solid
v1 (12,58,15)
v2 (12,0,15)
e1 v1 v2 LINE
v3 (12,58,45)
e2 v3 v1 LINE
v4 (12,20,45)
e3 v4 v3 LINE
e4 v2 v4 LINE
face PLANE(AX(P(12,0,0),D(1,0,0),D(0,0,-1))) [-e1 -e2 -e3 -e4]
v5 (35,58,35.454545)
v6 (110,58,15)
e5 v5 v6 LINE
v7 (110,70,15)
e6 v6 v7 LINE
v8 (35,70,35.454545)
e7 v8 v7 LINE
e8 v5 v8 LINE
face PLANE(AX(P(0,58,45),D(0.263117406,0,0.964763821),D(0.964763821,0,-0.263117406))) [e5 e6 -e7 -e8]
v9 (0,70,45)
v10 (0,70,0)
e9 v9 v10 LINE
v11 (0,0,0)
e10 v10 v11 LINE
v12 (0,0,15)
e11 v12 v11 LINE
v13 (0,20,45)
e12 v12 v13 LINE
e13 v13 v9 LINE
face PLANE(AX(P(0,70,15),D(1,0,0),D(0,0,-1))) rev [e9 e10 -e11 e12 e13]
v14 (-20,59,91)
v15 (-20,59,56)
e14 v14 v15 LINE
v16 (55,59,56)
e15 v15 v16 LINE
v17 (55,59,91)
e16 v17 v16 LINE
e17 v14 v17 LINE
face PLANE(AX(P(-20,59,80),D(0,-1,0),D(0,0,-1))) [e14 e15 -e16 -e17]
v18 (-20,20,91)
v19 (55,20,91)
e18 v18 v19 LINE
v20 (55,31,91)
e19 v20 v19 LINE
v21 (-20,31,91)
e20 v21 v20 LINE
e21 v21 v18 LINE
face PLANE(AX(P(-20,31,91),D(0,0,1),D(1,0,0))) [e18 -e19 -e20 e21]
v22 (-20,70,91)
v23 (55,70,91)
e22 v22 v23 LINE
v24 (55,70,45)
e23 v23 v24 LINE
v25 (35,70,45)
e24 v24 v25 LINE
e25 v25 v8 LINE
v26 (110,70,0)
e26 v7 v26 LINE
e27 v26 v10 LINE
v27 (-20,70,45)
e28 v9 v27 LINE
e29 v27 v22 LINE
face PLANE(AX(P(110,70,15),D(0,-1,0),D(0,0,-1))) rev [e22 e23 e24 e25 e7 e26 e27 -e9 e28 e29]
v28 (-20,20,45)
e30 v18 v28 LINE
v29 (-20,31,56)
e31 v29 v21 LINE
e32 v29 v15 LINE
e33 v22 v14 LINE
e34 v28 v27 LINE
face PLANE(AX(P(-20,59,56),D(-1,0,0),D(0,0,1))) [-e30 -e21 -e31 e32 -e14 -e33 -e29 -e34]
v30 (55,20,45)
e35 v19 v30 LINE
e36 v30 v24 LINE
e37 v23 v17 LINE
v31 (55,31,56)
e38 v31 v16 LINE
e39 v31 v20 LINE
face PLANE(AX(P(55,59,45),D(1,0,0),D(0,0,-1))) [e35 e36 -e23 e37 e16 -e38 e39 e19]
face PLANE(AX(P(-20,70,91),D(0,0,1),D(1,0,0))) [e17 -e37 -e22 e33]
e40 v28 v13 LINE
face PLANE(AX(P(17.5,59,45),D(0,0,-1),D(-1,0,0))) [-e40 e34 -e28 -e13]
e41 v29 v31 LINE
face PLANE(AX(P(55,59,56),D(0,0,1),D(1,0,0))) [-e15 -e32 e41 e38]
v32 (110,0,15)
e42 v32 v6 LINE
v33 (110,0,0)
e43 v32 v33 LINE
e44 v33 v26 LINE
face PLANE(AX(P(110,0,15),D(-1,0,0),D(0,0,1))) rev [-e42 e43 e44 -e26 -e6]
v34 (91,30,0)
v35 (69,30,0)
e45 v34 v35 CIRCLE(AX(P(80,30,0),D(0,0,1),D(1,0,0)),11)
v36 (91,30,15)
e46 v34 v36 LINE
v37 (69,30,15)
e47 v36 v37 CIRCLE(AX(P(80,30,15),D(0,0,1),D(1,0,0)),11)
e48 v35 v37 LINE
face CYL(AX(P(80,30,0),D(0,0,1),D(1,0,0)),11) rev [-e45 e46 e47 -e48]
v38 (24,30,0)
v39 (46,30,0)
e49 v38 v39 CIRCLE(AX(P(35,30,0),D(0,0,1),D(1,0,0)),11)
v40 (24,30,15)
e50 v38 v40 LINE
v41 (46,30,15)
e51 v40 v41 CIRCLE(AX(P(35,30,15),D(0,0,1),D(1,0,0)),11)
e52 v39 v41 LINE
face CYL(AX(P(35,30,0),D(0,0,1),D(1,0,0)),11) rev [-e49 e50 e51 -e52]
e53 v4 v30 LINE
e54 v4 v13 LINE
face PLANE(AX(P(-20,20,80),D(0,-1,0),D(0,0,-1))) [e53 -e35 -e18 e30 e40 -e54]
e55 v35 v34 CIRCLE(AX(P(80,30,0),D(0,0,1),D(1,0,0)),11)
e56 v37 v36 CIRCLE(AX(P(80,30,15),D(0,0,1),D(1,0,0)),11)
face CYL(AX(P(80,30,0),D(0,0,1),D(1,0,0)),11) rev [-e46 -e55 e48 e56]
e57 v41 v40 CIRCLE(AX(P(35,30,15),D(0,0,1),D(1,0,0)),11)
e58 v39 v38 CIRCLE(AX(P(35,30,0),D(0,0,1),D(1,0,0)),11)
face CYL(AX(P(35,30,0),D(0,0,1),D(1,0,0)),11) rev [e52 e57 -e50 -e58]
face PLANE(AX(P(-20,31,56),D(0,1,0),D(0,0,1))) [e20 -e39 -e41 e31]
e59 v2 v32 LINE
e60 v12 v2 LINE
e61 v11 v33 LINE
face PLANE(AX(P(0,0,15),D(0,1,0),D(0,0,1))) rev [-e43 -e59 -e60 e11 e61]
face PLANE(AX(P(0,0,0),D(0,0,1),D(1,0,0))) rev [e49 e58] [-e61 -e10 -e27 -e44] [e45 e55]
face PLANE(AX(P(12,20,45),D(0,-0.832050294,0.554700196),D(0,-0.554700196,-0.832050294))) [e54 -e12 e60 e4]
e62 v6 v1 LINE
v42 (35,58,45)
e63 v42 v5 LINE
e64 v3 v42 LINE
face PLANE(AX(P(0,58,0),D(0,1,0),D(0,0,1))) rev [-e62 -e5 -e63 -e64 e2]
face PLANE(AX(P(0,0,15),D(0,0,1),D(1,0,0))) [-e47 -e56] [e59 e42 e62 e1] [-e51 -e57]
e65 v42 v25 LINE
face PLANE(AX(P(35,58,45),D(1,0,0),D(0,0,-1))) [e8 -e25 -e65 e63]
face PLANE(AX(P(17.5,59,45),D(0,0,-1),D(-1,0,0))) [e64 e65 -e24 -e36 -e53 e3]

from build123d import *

# Parameters (mm, degrees)
BASE_PLATE_SKETCH_W         = 110
BASE_PLATE_SKETCH_H         = 70
BASE_PLATE_15MM_DEPTH       = 15
TRIANGULAR_WALL_12MM_DEPTH  = 12
WALL_EXTENSION_12MM_DEPTH   = 12
WEDGE_GUSSET_12MM_DEPTH     = 12
TOP_PROFILE_BOSS_11MM_DEPTH = 11
PROFILE_ARM_75MM_DEPTH      = 75
BLOCK_ARM_SKETCH_W          = 24
BLOCK_ARM_SKETCH_H          = 11
BLOCK_ARM_75MM_DEPTH        = 75
HOLE_CIRCLES_2X_22_SKETCH_R = 11
HOLES_2X_22_DEPTH           = 15
UPPER_JAW_SKETCH_W          = 11
UPPER_JAW_SKETCH_H          = 11
UPPER_JAW_75MM_DEPTH        = 75
LOWER_JAW_SKETCH_W          = 11
LOWER_JAW_SKETCH_H          = 11
LOWER_JAW_75MM_DEPTH        = 75


with BuildPart() as part:
    # Base Plate Sketch → Base Plate 15mm (new body)
    with BuildSketch(Plane.XY):
        with Locations((55, 35)):
            Rectangle(BASE_PLATE_SKETCH_W, BASE_PLATE_SKETCH_H)
    extrude(amount=BASE_PLATE_15MM_DEPTH)

    # Triangular Wall Sketch → Triangular Wall 12mm (add)
    with BuildSketch(Plane(origin=(0, 70, 0), x_dir=(1, 0, 0), z_dir=(0, 1, 0))):
        Polygon((0, -15), (0, -45), (110, -15), align=None)
    extrude(amount=-TRIANGULAR_WALL_12MM_DEPTH)

    # Wall Extension Sketch → Wall Extension 12mm (add)
    with BuildSketch(Plane.ZY):
        Polygon((45, 58), (45, 20), (15, 0), (15, 58), align=None)
    extrude(amount=-WALL_EXTENSION_12MM_DEPTH)

    # Wedge Gusset Sketch → Wedge Gusset 12mm (add)
    with BuildSketch(Plane(origin=(0, 70, 0), x_dir=(1, 0, 0), z_dir=(0, 1, 0))):
        Polygon((0, -45), (35, -45), (35, -35.454545455), align=None)
    extrude(amount=-WEDGE_GUSSET_12MM_DEPTH)

    # Top Profile Sketch → Top Profile Boss 11mm (add)
    with BuildSketch(Plane(origin=(0, 70, 0), x_dir=(1, 0, 0), z_dir=(0, 1, 0))):
        Polygon((17.5, -45), (55, -45), (55, -56), (-20, -56), (-20, -45), align=None)
    extrude(amount=-TOP_PROFILE_BOSS_11MM_DEPTH)

    # Profile Arm Sketch → Profile Arm 75mm (add)
    with BuildSketch(Plane(origin=(55, 0, 0), x_dir=(0, 0, -1), z_dir=(1, 0, 0))):
        Polygon((-45, 59), (-45, 31), (-45, 20), (-80, 20), (-80, 31), (-56, 31), (-56, 59), align=None)
    extrude(amount=-PROFILE_ARM_75MM_DEPTH)

    # Block Arm Sketch → Block Arm 75mm (add)
    with BuildSketch(Plane(origin=(55, 0, 0), x_dir=(0, 0, -1), z_dir=(1, 0, 0))):
        with Locations((-68, 64.5)):
            Rectangle(BLOCK_ARM_SKETCH_W, BLOCK_ARM_SKETCH_H)
    extrude(amount=-BLOCK_ARM_75MM_DEPTH)

    # Hole Circles 2xØ22 Sketch → Holes 2xØ22 (cut)
    with BuildSketch(Plane.XY.offset(15)):
        with Locations((80, 30)):
            Circle(HOLE_CIRCLES_2X_22_SKETCH_R)
        with Locations((35, 30)):
            Circle(HOLE_CIRCLES_2X_22_SKETCH_R)
    extrude(amount=-HOLES_2X_22_DEPTH, mode=Mode.SUBTRACT)

    # Upper Jaw Sketch → Upper Jaw 75mm (add)
    with BuildSketch(Plane(origin=(55, 0, 0), x_dir=(0, 0, -1), z_dir=(1, 0, 0))):
        with Locations((-85.5, 64.5)):
            Rectangle(UPPER_JAW_SKETCH_W, UPPER_JAW_SKETCH_H)
    extrude(amount=-UPPER_JAW_75MM_DEPTH)

    # Lower Jaw Sketch → Lower Jaw 75mm (add)
    with BuildSketch(Plane(origin=(55, 0, 0), x_dir=(0, 0, -1), z_dir=(1, 0, 0))):
        with Locations((-85.5, 25.5)):
            Rectangle(LOWER_JAW_SKETCH_W, LOWER_JAW_SKETCH_H)
    extrude(amount=-LOWER_JAW_75MM_DEPTH)


solid = part.part
